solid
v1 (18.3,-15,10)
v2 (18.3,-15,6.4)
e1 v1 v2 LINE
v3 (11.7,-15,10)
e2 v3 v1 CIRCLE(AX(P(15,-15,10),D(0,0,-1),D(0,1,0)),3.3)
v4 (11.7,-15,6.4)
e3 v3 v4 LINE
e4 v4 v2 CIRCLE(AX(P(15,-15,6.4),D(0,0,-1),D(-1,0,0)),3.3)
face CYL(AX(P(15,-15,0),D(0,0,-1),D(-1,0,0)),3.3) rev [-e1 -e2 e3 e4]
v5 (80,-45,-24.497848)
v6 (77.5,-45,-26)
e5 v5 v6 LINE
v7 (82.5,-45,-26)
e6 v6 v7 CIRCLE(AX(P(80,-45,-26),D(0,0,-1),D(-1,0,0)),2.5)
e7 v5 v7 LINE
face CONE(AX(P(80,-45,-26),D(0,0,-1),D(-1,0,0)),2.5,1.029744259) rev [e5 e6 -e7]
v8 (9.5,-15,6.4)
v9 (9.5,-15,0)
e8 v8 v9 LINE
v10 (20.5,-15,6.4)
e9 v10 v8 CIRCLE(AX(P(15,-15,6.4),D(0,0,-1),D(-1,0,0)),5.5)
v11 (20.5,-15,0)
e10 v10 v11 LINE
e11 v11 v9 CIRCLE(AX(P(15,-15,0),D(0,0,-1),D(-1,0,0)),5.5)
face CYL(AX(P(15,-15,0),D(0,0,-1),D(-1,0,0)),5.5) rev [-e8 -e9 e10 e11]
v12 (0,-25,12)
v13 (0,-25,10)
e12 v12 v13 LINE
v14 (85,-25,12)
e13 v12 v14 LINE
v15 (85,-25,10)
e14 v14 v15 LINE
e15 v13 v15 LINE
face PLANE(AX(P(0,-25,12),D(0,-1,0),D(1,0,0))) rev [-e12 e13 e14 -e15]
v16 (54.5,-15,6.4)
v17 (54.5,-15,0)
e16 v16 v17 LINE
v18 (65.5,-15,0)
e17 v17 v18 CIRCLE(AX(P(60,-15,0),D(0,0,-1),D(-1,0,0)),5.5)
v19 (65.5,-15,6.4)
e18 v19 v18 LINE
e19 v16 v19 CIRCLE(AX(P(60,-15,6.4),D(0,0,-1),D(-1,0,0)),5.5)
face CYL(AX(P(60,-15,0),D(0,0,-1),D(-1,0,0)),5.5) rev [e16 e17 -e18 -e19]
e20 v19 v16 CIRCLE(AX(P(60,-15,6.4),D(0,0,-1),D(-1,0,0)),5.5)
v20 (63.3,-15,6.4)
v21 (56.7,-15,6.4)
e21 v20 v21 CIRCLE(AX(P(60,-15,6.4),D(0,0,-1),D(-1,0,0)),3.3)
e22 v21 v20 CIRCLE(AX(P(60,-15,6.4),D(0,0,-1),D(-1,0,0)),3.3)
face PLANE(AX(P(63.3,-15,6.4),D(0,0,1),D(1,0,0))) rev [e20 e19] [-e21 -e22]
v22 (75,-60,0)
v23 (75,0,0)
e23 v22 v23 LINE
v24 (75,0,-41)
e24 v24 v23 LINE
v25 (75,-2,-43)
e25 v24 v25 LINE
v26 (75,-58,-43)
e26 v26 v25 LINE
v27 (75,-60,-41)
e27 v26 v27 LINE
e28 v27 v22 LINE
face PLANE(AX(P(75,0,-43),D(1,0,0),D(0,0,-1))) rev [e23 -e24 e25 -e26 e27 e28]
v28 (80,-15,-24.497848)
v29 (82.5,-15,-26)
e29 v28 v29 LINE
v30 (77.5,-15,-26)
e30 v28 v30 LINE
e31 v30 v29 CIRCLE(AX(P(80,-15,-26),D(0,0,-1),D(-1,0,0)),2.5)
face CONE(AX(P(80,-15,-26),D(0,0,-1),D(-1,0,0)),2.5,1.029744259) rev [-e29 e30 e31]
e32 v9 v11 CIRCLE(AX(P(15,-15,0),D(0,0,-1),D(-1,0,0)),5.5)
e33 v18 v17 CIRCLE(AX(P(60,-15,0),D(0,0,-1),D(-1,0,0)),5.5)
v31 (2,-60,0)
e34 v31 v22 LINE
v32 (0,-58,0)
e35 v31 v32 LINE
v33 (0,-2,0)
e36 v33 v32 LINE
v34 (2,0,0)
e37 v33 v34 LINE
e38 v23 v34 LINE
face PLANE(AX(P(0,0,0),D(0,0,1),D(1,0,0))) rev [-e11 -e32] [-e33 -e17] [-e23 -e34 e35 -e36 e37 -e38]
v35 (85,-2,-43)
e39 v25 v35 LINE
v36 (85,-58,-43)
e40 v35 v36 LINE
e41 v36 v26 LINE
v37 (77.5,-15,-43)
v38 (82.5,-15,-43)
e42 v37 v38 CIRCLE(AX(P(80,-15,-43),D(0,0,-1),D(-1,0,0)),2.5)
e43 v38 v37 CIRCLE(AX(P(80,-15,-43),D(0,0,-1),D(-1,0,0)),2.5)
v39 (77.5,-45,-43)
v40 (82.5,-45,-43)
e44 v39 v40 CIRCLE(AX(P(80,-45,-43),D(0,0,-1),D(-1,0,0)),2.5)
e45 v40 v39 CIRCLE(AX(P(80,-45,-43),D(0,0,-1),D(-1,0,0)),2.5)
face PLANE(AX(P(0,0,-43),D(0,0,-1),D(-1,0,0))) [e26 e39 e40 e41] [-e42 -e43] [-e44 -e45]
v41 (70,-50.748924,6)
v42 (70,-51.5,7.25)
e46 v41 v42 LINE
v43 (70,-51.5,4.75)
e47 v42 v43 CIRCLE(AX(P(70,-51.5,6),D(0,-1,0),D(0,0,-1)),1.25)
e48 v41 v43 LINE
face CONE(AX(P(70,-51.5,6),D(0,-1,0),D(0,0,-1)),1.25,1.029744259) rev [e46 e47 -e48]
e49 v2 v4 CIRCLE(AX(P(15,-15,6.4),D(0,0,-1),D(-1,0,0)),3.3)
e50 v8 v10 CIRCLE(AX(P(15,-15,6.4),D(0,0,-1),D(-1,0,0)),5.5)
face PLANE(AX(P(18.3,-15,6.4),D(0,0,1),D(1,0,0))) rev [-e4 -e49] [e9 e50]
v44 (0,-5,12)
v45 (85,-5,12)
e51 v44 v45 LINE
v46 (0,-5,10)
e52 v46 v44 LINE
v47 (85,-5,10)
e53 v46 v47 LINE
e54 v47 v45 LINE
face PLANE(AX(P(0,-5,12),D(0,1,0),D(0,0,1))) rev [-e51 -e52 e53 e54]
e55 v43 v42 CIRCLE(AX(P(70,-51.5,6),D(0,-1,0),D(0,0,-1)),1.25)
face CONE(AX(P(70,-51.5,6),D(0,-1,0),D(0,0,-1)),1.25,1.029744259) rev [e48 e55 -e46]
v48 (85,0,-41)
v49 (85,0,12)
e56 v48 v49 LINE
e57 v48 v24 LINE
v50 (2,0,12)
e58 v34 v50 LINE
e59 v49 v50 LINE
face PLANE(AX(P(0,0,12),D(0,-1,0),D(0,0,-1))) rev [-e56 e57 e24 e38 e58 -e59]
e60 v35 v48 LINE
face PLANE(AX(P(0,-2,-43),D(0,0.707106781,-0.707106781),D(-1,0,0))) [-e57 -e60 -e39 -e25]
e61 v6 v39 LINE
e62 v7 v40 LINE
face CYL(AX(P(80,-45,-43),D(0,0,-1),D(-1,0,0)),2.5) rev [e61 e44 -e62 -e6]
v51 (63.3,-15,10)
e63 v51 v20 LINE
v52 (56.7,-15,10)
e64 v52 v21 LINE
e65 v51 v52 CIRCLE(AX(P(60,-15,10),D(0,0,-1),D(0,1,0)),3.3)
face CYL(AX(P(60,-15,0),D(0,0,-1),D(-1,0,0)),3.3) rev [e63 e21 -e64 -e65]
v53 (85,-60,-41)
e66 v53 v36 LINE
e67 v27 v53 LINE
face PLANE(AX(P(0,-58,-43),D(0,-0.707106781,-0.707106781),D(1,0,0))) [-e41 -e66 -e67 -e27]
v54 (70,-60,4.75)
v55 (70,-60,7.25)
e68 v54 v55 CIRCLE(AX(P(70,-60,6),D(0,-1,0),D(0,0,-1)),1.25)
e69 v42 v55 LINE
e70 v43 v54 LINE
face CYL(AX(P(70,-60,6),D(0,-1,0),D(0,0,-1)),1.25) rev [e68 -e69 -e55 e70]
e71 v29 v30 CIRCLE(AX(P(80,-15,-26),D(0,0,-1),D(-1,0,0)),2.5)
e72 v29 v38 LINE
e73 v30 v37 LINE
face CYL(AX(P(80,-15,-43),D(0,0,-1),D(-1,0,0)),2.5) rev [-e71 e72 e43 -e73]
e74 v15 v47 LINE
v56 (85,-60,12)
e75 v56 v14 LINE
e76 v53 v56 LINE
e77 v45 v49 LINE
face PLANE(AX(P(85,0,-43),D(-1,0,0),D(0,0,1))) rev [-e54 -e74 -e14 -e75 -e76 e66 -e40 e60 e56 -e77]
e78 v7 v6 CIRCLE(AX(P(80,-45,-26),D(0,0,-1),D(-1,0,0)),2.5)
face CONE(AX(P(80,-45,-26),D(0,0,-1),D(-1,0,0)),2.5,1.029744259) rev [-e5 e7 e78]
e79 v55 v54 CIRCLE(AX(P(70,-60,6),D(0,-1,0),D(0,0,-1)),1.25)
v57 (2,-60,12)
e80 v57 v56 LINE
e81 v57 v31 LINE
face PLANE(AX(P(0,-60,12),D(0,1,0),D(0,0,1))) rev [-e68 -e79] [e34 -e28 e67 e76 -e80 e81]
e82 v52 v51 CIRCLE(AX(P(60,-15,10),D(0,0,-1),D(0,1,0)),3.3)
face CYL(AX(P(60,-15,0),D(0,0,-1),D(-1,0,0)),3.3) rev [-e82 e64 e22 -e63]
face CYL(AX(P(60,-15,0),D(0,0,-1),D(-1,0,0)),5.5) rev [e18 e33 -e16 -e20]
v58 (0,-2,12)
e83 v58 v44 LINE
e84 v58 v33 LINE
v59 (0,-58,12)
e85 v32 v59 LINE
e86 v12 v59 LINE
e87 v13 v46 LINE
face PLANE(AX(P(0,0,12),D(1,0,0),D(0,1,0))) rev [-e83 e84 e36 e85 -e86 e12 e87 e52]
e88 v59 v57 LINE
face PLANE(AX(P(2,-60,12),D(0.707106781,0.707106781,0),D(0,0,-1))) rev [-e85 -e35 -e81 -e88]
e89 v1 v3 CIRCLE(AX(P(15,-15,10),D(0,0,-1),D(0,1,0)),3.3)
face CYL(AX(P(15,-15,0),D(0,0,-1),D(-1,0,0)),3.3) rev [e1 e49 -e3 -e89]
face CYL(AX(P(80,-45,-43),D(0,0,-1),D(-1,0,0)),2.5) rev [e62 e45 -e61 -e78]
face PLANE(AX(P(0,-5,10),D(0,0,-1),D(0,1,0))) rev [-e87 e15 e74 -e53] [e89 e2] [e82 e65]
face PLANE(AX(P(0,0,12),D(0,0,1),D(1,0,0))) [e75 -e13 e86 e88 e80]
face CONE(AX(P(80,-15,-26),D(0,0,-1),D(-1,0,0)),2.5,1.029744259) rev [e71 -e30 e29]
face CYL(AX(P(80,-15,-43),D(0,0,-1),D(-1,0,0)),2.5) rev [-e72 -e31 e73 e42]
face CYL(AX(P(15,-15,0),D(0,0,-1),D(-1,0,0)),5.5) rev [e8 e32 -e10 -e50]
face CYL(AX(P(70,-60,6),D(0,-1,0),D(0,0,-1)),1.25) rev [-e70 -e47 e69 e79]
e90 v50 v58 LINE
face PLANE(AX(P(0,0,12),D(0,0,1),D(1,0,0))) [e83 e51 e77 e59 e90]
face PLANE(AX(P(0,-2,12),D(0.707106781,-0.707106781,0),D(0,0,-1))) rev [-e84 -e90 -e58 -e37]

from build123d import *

# Parameters (mm, degrees)
SKETCH_2_W                   = 90
SKETCH_2_H                   = 60
EXTRUDE_1_DEPTH              = 12
SKETCH_3_W                   = 2
SKETCH_3_H                   = 20
CUT_EXTRUDE_1_DEPTH          = 109.830142883
SKETCH_4_W                   = 10
SKETCH_4_H                   = 1
CUT_EXTRUDE_2_DEPTH          = 109.830142883
HOLE_WIZARD_M6_3_D           = 6.6
HOLE_WIZARD_M6_3_DEPTH       = 17
HOLE_WIZARD_M6_3_CBORE_D     = 11
HOLE_WIZARD_M6_3_CBORE_DEPTH = 6.4
HOLE_WIZARD_M6_3_TIP         = 1.982840043
CHAMFER_1_SIZE               = 2
HOLE_WIZARD_M3_1_D           = 2.5
HOLE_WIZARD_M3_1_DEPTH       = 8.5
HOLE_WIZARD_M3_1_TIP         = 0.751075774
SKETCH_15_W                  = 10
SKETCH_15_H                  = 60
EXTRUDE_2_DEPTH              = 44
SKETCH_16_W                  = 5
SKETCH_16_H                  = 60
CUT_EXTRUDE_3_DEPTH          = 117.400171821
HOLE_WIZARD_M6_1_D           = 5
HOLE_WIZARD_M6_1_DEPTH       = 17
HOLE_WIZARD_M6_1_TIP         = 1.502151548
CHAMFER_2_SIZE               = 2


with BuildPart() as part:
    # 草图2 → 凸台-拉伸1 (new body)
    with BuildSketch(Plane.XY):
        with Locations((45, -30)):
            Rectangle(SKETCH_2_W, SKETCH_2_H)
    extrude(amount=EXTRUDE_1_DEPTH)

    # 草图3 → 切除-拉伸1 (cut, through all)
    with BuildSketch(Plane(origin=(90, 0, 0), x_dir=(0, 0, -1), z_dir=(1, 0, 0))):
        with Locations((-11, -15)):
            Rectangle(SKETCH_3_W, SKETCH_3_H)
    extrude(amount=-CUT_EXTRUDE_1_DEPTH, mode=Mode.SUBTRACT)

    # 草图4 → 切除-拉伸2 (cut, through all)
    with BuildSketch(Plane(origin=(0, 0, 0), x_dir=(1, 0, 0), z_dir=(0, 1, 0))):
        with Locations((80, -0.5)):
            Rectangle(SKETCH_4_W, SKETCH_4_H)
    extrude(amount=-CUT_EXTRUDE_2_DEPTH, mode=Mode.SUBTRACT)

    # M6 六角凹头螺钉的柱形沉头孔3
    with Locations(Plane(origin=(0, 0, 0), x_dir=(-1, 0, 0), z_dir=(0, 0, -1))):
        with Locations((-60, -15), (-15, -15)):
            CounterBoreHole(HOLE_WIZARD_M6_3_D / 2, HOLE_WIZARD_M6_3_CBORE_D / 2, HOLE_WIZARD_M6_3_CBORE_DEPTH, depth=HOLE_WIZARD_M6_3_DEPTH)
            with Locations((0, 0, -(HOLE_WIZARD_M6_3_DEPTH + HOLE_WIZARD_M6_3_TIP / 2))):  # 118° drill point
                Cone(0, HOLE_WIZARD_M6_3_D / 2, HOLE_WIZARD_M6_3_TIP, mode=Mode.SUBTRACT)

    # 倒角1
    chamfer_1_edges = [part.edges().sort_by_distance(p)[0] for p in [
        (0, 0, 6),
        (90, 0, 6),
        (90, -60, 6),
        (0, -60, 6),
    ]]
    chamfer(chamfer_1_edges, length=CHAMFER_1_SIZE)

    # M3 螺纹孔1
    with Locations(Plane(origin=(0, -60, 0), x_dir=(-1, 0, 0), z_dir=(0, -1, 0))):
        with Locations((-70, -6)):
            Hole(HOLE_WIZARD_M3_1_D / 2, depth=HOLE_WIZARD_M3_1_DEPTH)
            with Locations((0, 0, -(HOLE_WIZARD_M3_1_DEPTH + HOLE_WIZARD_M3_1_TIP / 2))):  # 118° drill point
                Cone(0, HOLE_WIZARD_M3_1_D / 2, HOLE_WIZARD_M3_1_TIP, mode=Mode.SUBTRACT)

    # 草图15 → 凸台-拉伸2 (add)
    with BuildSketch(Plane(origin=(0, 0, 1), x_dir=(-1, 0, 0), z_dir=(0, 0, -1))):
        with Locations((-80, -30)):
            Rectangle(SKETCH_15_W, SKETCH_15_H)
    extrude(amount=EXTRUDE_2_DEPTH)

    # 草图16 → 切除-拉伸3 (cut, through all)
    with BuildSketch(Plane(origin=(0, 0, 0), x_dir=(-1, 0, 0), z_dir=(0, 0, -1))):
        with Locations((-87.5, -30)):
            Rectangle(SKETCH_16_W, SKETCH_16_H)
    extrude(amount=-CUT_EXTRUDE_3_DEPTH, mode=Mode.SUBTRACT)

    # M6 螺纹孔1
    with Locations(Plane(origin=(0, 0, -43), x_dir=(-1, 0, 0), z_dir=(0, 0, -1))):
        with Locations((-80, -15), (-80, -45)):
            Hole(HOLE_WIZARD_M6_1_D / 2, depth=HOLE_WIZARD_M6_1_DEPTH)
            with Locations((0, 0, -(HOLE_WIZARD_M6_1_DEPTH + HOLE_WIZARD_M6_1_TIP / 2))):  # 118° drill point
                Cone(0, HOLE_WIZARD_M6_1_D / 2, HOLE_WIZARD_M6_1_TIP, mode=Mode.SUBTRACT)

    # 倒角2
    chamfer_2_edges = [part.edges().sort_by_distance(p)[0] for p in [
        (80, -60, -43),
        (80, 0, -43),
    ]]
    chamfer(chamfer_2_edges, length=CHAMFER_2_SIZE)


solid = part.part
